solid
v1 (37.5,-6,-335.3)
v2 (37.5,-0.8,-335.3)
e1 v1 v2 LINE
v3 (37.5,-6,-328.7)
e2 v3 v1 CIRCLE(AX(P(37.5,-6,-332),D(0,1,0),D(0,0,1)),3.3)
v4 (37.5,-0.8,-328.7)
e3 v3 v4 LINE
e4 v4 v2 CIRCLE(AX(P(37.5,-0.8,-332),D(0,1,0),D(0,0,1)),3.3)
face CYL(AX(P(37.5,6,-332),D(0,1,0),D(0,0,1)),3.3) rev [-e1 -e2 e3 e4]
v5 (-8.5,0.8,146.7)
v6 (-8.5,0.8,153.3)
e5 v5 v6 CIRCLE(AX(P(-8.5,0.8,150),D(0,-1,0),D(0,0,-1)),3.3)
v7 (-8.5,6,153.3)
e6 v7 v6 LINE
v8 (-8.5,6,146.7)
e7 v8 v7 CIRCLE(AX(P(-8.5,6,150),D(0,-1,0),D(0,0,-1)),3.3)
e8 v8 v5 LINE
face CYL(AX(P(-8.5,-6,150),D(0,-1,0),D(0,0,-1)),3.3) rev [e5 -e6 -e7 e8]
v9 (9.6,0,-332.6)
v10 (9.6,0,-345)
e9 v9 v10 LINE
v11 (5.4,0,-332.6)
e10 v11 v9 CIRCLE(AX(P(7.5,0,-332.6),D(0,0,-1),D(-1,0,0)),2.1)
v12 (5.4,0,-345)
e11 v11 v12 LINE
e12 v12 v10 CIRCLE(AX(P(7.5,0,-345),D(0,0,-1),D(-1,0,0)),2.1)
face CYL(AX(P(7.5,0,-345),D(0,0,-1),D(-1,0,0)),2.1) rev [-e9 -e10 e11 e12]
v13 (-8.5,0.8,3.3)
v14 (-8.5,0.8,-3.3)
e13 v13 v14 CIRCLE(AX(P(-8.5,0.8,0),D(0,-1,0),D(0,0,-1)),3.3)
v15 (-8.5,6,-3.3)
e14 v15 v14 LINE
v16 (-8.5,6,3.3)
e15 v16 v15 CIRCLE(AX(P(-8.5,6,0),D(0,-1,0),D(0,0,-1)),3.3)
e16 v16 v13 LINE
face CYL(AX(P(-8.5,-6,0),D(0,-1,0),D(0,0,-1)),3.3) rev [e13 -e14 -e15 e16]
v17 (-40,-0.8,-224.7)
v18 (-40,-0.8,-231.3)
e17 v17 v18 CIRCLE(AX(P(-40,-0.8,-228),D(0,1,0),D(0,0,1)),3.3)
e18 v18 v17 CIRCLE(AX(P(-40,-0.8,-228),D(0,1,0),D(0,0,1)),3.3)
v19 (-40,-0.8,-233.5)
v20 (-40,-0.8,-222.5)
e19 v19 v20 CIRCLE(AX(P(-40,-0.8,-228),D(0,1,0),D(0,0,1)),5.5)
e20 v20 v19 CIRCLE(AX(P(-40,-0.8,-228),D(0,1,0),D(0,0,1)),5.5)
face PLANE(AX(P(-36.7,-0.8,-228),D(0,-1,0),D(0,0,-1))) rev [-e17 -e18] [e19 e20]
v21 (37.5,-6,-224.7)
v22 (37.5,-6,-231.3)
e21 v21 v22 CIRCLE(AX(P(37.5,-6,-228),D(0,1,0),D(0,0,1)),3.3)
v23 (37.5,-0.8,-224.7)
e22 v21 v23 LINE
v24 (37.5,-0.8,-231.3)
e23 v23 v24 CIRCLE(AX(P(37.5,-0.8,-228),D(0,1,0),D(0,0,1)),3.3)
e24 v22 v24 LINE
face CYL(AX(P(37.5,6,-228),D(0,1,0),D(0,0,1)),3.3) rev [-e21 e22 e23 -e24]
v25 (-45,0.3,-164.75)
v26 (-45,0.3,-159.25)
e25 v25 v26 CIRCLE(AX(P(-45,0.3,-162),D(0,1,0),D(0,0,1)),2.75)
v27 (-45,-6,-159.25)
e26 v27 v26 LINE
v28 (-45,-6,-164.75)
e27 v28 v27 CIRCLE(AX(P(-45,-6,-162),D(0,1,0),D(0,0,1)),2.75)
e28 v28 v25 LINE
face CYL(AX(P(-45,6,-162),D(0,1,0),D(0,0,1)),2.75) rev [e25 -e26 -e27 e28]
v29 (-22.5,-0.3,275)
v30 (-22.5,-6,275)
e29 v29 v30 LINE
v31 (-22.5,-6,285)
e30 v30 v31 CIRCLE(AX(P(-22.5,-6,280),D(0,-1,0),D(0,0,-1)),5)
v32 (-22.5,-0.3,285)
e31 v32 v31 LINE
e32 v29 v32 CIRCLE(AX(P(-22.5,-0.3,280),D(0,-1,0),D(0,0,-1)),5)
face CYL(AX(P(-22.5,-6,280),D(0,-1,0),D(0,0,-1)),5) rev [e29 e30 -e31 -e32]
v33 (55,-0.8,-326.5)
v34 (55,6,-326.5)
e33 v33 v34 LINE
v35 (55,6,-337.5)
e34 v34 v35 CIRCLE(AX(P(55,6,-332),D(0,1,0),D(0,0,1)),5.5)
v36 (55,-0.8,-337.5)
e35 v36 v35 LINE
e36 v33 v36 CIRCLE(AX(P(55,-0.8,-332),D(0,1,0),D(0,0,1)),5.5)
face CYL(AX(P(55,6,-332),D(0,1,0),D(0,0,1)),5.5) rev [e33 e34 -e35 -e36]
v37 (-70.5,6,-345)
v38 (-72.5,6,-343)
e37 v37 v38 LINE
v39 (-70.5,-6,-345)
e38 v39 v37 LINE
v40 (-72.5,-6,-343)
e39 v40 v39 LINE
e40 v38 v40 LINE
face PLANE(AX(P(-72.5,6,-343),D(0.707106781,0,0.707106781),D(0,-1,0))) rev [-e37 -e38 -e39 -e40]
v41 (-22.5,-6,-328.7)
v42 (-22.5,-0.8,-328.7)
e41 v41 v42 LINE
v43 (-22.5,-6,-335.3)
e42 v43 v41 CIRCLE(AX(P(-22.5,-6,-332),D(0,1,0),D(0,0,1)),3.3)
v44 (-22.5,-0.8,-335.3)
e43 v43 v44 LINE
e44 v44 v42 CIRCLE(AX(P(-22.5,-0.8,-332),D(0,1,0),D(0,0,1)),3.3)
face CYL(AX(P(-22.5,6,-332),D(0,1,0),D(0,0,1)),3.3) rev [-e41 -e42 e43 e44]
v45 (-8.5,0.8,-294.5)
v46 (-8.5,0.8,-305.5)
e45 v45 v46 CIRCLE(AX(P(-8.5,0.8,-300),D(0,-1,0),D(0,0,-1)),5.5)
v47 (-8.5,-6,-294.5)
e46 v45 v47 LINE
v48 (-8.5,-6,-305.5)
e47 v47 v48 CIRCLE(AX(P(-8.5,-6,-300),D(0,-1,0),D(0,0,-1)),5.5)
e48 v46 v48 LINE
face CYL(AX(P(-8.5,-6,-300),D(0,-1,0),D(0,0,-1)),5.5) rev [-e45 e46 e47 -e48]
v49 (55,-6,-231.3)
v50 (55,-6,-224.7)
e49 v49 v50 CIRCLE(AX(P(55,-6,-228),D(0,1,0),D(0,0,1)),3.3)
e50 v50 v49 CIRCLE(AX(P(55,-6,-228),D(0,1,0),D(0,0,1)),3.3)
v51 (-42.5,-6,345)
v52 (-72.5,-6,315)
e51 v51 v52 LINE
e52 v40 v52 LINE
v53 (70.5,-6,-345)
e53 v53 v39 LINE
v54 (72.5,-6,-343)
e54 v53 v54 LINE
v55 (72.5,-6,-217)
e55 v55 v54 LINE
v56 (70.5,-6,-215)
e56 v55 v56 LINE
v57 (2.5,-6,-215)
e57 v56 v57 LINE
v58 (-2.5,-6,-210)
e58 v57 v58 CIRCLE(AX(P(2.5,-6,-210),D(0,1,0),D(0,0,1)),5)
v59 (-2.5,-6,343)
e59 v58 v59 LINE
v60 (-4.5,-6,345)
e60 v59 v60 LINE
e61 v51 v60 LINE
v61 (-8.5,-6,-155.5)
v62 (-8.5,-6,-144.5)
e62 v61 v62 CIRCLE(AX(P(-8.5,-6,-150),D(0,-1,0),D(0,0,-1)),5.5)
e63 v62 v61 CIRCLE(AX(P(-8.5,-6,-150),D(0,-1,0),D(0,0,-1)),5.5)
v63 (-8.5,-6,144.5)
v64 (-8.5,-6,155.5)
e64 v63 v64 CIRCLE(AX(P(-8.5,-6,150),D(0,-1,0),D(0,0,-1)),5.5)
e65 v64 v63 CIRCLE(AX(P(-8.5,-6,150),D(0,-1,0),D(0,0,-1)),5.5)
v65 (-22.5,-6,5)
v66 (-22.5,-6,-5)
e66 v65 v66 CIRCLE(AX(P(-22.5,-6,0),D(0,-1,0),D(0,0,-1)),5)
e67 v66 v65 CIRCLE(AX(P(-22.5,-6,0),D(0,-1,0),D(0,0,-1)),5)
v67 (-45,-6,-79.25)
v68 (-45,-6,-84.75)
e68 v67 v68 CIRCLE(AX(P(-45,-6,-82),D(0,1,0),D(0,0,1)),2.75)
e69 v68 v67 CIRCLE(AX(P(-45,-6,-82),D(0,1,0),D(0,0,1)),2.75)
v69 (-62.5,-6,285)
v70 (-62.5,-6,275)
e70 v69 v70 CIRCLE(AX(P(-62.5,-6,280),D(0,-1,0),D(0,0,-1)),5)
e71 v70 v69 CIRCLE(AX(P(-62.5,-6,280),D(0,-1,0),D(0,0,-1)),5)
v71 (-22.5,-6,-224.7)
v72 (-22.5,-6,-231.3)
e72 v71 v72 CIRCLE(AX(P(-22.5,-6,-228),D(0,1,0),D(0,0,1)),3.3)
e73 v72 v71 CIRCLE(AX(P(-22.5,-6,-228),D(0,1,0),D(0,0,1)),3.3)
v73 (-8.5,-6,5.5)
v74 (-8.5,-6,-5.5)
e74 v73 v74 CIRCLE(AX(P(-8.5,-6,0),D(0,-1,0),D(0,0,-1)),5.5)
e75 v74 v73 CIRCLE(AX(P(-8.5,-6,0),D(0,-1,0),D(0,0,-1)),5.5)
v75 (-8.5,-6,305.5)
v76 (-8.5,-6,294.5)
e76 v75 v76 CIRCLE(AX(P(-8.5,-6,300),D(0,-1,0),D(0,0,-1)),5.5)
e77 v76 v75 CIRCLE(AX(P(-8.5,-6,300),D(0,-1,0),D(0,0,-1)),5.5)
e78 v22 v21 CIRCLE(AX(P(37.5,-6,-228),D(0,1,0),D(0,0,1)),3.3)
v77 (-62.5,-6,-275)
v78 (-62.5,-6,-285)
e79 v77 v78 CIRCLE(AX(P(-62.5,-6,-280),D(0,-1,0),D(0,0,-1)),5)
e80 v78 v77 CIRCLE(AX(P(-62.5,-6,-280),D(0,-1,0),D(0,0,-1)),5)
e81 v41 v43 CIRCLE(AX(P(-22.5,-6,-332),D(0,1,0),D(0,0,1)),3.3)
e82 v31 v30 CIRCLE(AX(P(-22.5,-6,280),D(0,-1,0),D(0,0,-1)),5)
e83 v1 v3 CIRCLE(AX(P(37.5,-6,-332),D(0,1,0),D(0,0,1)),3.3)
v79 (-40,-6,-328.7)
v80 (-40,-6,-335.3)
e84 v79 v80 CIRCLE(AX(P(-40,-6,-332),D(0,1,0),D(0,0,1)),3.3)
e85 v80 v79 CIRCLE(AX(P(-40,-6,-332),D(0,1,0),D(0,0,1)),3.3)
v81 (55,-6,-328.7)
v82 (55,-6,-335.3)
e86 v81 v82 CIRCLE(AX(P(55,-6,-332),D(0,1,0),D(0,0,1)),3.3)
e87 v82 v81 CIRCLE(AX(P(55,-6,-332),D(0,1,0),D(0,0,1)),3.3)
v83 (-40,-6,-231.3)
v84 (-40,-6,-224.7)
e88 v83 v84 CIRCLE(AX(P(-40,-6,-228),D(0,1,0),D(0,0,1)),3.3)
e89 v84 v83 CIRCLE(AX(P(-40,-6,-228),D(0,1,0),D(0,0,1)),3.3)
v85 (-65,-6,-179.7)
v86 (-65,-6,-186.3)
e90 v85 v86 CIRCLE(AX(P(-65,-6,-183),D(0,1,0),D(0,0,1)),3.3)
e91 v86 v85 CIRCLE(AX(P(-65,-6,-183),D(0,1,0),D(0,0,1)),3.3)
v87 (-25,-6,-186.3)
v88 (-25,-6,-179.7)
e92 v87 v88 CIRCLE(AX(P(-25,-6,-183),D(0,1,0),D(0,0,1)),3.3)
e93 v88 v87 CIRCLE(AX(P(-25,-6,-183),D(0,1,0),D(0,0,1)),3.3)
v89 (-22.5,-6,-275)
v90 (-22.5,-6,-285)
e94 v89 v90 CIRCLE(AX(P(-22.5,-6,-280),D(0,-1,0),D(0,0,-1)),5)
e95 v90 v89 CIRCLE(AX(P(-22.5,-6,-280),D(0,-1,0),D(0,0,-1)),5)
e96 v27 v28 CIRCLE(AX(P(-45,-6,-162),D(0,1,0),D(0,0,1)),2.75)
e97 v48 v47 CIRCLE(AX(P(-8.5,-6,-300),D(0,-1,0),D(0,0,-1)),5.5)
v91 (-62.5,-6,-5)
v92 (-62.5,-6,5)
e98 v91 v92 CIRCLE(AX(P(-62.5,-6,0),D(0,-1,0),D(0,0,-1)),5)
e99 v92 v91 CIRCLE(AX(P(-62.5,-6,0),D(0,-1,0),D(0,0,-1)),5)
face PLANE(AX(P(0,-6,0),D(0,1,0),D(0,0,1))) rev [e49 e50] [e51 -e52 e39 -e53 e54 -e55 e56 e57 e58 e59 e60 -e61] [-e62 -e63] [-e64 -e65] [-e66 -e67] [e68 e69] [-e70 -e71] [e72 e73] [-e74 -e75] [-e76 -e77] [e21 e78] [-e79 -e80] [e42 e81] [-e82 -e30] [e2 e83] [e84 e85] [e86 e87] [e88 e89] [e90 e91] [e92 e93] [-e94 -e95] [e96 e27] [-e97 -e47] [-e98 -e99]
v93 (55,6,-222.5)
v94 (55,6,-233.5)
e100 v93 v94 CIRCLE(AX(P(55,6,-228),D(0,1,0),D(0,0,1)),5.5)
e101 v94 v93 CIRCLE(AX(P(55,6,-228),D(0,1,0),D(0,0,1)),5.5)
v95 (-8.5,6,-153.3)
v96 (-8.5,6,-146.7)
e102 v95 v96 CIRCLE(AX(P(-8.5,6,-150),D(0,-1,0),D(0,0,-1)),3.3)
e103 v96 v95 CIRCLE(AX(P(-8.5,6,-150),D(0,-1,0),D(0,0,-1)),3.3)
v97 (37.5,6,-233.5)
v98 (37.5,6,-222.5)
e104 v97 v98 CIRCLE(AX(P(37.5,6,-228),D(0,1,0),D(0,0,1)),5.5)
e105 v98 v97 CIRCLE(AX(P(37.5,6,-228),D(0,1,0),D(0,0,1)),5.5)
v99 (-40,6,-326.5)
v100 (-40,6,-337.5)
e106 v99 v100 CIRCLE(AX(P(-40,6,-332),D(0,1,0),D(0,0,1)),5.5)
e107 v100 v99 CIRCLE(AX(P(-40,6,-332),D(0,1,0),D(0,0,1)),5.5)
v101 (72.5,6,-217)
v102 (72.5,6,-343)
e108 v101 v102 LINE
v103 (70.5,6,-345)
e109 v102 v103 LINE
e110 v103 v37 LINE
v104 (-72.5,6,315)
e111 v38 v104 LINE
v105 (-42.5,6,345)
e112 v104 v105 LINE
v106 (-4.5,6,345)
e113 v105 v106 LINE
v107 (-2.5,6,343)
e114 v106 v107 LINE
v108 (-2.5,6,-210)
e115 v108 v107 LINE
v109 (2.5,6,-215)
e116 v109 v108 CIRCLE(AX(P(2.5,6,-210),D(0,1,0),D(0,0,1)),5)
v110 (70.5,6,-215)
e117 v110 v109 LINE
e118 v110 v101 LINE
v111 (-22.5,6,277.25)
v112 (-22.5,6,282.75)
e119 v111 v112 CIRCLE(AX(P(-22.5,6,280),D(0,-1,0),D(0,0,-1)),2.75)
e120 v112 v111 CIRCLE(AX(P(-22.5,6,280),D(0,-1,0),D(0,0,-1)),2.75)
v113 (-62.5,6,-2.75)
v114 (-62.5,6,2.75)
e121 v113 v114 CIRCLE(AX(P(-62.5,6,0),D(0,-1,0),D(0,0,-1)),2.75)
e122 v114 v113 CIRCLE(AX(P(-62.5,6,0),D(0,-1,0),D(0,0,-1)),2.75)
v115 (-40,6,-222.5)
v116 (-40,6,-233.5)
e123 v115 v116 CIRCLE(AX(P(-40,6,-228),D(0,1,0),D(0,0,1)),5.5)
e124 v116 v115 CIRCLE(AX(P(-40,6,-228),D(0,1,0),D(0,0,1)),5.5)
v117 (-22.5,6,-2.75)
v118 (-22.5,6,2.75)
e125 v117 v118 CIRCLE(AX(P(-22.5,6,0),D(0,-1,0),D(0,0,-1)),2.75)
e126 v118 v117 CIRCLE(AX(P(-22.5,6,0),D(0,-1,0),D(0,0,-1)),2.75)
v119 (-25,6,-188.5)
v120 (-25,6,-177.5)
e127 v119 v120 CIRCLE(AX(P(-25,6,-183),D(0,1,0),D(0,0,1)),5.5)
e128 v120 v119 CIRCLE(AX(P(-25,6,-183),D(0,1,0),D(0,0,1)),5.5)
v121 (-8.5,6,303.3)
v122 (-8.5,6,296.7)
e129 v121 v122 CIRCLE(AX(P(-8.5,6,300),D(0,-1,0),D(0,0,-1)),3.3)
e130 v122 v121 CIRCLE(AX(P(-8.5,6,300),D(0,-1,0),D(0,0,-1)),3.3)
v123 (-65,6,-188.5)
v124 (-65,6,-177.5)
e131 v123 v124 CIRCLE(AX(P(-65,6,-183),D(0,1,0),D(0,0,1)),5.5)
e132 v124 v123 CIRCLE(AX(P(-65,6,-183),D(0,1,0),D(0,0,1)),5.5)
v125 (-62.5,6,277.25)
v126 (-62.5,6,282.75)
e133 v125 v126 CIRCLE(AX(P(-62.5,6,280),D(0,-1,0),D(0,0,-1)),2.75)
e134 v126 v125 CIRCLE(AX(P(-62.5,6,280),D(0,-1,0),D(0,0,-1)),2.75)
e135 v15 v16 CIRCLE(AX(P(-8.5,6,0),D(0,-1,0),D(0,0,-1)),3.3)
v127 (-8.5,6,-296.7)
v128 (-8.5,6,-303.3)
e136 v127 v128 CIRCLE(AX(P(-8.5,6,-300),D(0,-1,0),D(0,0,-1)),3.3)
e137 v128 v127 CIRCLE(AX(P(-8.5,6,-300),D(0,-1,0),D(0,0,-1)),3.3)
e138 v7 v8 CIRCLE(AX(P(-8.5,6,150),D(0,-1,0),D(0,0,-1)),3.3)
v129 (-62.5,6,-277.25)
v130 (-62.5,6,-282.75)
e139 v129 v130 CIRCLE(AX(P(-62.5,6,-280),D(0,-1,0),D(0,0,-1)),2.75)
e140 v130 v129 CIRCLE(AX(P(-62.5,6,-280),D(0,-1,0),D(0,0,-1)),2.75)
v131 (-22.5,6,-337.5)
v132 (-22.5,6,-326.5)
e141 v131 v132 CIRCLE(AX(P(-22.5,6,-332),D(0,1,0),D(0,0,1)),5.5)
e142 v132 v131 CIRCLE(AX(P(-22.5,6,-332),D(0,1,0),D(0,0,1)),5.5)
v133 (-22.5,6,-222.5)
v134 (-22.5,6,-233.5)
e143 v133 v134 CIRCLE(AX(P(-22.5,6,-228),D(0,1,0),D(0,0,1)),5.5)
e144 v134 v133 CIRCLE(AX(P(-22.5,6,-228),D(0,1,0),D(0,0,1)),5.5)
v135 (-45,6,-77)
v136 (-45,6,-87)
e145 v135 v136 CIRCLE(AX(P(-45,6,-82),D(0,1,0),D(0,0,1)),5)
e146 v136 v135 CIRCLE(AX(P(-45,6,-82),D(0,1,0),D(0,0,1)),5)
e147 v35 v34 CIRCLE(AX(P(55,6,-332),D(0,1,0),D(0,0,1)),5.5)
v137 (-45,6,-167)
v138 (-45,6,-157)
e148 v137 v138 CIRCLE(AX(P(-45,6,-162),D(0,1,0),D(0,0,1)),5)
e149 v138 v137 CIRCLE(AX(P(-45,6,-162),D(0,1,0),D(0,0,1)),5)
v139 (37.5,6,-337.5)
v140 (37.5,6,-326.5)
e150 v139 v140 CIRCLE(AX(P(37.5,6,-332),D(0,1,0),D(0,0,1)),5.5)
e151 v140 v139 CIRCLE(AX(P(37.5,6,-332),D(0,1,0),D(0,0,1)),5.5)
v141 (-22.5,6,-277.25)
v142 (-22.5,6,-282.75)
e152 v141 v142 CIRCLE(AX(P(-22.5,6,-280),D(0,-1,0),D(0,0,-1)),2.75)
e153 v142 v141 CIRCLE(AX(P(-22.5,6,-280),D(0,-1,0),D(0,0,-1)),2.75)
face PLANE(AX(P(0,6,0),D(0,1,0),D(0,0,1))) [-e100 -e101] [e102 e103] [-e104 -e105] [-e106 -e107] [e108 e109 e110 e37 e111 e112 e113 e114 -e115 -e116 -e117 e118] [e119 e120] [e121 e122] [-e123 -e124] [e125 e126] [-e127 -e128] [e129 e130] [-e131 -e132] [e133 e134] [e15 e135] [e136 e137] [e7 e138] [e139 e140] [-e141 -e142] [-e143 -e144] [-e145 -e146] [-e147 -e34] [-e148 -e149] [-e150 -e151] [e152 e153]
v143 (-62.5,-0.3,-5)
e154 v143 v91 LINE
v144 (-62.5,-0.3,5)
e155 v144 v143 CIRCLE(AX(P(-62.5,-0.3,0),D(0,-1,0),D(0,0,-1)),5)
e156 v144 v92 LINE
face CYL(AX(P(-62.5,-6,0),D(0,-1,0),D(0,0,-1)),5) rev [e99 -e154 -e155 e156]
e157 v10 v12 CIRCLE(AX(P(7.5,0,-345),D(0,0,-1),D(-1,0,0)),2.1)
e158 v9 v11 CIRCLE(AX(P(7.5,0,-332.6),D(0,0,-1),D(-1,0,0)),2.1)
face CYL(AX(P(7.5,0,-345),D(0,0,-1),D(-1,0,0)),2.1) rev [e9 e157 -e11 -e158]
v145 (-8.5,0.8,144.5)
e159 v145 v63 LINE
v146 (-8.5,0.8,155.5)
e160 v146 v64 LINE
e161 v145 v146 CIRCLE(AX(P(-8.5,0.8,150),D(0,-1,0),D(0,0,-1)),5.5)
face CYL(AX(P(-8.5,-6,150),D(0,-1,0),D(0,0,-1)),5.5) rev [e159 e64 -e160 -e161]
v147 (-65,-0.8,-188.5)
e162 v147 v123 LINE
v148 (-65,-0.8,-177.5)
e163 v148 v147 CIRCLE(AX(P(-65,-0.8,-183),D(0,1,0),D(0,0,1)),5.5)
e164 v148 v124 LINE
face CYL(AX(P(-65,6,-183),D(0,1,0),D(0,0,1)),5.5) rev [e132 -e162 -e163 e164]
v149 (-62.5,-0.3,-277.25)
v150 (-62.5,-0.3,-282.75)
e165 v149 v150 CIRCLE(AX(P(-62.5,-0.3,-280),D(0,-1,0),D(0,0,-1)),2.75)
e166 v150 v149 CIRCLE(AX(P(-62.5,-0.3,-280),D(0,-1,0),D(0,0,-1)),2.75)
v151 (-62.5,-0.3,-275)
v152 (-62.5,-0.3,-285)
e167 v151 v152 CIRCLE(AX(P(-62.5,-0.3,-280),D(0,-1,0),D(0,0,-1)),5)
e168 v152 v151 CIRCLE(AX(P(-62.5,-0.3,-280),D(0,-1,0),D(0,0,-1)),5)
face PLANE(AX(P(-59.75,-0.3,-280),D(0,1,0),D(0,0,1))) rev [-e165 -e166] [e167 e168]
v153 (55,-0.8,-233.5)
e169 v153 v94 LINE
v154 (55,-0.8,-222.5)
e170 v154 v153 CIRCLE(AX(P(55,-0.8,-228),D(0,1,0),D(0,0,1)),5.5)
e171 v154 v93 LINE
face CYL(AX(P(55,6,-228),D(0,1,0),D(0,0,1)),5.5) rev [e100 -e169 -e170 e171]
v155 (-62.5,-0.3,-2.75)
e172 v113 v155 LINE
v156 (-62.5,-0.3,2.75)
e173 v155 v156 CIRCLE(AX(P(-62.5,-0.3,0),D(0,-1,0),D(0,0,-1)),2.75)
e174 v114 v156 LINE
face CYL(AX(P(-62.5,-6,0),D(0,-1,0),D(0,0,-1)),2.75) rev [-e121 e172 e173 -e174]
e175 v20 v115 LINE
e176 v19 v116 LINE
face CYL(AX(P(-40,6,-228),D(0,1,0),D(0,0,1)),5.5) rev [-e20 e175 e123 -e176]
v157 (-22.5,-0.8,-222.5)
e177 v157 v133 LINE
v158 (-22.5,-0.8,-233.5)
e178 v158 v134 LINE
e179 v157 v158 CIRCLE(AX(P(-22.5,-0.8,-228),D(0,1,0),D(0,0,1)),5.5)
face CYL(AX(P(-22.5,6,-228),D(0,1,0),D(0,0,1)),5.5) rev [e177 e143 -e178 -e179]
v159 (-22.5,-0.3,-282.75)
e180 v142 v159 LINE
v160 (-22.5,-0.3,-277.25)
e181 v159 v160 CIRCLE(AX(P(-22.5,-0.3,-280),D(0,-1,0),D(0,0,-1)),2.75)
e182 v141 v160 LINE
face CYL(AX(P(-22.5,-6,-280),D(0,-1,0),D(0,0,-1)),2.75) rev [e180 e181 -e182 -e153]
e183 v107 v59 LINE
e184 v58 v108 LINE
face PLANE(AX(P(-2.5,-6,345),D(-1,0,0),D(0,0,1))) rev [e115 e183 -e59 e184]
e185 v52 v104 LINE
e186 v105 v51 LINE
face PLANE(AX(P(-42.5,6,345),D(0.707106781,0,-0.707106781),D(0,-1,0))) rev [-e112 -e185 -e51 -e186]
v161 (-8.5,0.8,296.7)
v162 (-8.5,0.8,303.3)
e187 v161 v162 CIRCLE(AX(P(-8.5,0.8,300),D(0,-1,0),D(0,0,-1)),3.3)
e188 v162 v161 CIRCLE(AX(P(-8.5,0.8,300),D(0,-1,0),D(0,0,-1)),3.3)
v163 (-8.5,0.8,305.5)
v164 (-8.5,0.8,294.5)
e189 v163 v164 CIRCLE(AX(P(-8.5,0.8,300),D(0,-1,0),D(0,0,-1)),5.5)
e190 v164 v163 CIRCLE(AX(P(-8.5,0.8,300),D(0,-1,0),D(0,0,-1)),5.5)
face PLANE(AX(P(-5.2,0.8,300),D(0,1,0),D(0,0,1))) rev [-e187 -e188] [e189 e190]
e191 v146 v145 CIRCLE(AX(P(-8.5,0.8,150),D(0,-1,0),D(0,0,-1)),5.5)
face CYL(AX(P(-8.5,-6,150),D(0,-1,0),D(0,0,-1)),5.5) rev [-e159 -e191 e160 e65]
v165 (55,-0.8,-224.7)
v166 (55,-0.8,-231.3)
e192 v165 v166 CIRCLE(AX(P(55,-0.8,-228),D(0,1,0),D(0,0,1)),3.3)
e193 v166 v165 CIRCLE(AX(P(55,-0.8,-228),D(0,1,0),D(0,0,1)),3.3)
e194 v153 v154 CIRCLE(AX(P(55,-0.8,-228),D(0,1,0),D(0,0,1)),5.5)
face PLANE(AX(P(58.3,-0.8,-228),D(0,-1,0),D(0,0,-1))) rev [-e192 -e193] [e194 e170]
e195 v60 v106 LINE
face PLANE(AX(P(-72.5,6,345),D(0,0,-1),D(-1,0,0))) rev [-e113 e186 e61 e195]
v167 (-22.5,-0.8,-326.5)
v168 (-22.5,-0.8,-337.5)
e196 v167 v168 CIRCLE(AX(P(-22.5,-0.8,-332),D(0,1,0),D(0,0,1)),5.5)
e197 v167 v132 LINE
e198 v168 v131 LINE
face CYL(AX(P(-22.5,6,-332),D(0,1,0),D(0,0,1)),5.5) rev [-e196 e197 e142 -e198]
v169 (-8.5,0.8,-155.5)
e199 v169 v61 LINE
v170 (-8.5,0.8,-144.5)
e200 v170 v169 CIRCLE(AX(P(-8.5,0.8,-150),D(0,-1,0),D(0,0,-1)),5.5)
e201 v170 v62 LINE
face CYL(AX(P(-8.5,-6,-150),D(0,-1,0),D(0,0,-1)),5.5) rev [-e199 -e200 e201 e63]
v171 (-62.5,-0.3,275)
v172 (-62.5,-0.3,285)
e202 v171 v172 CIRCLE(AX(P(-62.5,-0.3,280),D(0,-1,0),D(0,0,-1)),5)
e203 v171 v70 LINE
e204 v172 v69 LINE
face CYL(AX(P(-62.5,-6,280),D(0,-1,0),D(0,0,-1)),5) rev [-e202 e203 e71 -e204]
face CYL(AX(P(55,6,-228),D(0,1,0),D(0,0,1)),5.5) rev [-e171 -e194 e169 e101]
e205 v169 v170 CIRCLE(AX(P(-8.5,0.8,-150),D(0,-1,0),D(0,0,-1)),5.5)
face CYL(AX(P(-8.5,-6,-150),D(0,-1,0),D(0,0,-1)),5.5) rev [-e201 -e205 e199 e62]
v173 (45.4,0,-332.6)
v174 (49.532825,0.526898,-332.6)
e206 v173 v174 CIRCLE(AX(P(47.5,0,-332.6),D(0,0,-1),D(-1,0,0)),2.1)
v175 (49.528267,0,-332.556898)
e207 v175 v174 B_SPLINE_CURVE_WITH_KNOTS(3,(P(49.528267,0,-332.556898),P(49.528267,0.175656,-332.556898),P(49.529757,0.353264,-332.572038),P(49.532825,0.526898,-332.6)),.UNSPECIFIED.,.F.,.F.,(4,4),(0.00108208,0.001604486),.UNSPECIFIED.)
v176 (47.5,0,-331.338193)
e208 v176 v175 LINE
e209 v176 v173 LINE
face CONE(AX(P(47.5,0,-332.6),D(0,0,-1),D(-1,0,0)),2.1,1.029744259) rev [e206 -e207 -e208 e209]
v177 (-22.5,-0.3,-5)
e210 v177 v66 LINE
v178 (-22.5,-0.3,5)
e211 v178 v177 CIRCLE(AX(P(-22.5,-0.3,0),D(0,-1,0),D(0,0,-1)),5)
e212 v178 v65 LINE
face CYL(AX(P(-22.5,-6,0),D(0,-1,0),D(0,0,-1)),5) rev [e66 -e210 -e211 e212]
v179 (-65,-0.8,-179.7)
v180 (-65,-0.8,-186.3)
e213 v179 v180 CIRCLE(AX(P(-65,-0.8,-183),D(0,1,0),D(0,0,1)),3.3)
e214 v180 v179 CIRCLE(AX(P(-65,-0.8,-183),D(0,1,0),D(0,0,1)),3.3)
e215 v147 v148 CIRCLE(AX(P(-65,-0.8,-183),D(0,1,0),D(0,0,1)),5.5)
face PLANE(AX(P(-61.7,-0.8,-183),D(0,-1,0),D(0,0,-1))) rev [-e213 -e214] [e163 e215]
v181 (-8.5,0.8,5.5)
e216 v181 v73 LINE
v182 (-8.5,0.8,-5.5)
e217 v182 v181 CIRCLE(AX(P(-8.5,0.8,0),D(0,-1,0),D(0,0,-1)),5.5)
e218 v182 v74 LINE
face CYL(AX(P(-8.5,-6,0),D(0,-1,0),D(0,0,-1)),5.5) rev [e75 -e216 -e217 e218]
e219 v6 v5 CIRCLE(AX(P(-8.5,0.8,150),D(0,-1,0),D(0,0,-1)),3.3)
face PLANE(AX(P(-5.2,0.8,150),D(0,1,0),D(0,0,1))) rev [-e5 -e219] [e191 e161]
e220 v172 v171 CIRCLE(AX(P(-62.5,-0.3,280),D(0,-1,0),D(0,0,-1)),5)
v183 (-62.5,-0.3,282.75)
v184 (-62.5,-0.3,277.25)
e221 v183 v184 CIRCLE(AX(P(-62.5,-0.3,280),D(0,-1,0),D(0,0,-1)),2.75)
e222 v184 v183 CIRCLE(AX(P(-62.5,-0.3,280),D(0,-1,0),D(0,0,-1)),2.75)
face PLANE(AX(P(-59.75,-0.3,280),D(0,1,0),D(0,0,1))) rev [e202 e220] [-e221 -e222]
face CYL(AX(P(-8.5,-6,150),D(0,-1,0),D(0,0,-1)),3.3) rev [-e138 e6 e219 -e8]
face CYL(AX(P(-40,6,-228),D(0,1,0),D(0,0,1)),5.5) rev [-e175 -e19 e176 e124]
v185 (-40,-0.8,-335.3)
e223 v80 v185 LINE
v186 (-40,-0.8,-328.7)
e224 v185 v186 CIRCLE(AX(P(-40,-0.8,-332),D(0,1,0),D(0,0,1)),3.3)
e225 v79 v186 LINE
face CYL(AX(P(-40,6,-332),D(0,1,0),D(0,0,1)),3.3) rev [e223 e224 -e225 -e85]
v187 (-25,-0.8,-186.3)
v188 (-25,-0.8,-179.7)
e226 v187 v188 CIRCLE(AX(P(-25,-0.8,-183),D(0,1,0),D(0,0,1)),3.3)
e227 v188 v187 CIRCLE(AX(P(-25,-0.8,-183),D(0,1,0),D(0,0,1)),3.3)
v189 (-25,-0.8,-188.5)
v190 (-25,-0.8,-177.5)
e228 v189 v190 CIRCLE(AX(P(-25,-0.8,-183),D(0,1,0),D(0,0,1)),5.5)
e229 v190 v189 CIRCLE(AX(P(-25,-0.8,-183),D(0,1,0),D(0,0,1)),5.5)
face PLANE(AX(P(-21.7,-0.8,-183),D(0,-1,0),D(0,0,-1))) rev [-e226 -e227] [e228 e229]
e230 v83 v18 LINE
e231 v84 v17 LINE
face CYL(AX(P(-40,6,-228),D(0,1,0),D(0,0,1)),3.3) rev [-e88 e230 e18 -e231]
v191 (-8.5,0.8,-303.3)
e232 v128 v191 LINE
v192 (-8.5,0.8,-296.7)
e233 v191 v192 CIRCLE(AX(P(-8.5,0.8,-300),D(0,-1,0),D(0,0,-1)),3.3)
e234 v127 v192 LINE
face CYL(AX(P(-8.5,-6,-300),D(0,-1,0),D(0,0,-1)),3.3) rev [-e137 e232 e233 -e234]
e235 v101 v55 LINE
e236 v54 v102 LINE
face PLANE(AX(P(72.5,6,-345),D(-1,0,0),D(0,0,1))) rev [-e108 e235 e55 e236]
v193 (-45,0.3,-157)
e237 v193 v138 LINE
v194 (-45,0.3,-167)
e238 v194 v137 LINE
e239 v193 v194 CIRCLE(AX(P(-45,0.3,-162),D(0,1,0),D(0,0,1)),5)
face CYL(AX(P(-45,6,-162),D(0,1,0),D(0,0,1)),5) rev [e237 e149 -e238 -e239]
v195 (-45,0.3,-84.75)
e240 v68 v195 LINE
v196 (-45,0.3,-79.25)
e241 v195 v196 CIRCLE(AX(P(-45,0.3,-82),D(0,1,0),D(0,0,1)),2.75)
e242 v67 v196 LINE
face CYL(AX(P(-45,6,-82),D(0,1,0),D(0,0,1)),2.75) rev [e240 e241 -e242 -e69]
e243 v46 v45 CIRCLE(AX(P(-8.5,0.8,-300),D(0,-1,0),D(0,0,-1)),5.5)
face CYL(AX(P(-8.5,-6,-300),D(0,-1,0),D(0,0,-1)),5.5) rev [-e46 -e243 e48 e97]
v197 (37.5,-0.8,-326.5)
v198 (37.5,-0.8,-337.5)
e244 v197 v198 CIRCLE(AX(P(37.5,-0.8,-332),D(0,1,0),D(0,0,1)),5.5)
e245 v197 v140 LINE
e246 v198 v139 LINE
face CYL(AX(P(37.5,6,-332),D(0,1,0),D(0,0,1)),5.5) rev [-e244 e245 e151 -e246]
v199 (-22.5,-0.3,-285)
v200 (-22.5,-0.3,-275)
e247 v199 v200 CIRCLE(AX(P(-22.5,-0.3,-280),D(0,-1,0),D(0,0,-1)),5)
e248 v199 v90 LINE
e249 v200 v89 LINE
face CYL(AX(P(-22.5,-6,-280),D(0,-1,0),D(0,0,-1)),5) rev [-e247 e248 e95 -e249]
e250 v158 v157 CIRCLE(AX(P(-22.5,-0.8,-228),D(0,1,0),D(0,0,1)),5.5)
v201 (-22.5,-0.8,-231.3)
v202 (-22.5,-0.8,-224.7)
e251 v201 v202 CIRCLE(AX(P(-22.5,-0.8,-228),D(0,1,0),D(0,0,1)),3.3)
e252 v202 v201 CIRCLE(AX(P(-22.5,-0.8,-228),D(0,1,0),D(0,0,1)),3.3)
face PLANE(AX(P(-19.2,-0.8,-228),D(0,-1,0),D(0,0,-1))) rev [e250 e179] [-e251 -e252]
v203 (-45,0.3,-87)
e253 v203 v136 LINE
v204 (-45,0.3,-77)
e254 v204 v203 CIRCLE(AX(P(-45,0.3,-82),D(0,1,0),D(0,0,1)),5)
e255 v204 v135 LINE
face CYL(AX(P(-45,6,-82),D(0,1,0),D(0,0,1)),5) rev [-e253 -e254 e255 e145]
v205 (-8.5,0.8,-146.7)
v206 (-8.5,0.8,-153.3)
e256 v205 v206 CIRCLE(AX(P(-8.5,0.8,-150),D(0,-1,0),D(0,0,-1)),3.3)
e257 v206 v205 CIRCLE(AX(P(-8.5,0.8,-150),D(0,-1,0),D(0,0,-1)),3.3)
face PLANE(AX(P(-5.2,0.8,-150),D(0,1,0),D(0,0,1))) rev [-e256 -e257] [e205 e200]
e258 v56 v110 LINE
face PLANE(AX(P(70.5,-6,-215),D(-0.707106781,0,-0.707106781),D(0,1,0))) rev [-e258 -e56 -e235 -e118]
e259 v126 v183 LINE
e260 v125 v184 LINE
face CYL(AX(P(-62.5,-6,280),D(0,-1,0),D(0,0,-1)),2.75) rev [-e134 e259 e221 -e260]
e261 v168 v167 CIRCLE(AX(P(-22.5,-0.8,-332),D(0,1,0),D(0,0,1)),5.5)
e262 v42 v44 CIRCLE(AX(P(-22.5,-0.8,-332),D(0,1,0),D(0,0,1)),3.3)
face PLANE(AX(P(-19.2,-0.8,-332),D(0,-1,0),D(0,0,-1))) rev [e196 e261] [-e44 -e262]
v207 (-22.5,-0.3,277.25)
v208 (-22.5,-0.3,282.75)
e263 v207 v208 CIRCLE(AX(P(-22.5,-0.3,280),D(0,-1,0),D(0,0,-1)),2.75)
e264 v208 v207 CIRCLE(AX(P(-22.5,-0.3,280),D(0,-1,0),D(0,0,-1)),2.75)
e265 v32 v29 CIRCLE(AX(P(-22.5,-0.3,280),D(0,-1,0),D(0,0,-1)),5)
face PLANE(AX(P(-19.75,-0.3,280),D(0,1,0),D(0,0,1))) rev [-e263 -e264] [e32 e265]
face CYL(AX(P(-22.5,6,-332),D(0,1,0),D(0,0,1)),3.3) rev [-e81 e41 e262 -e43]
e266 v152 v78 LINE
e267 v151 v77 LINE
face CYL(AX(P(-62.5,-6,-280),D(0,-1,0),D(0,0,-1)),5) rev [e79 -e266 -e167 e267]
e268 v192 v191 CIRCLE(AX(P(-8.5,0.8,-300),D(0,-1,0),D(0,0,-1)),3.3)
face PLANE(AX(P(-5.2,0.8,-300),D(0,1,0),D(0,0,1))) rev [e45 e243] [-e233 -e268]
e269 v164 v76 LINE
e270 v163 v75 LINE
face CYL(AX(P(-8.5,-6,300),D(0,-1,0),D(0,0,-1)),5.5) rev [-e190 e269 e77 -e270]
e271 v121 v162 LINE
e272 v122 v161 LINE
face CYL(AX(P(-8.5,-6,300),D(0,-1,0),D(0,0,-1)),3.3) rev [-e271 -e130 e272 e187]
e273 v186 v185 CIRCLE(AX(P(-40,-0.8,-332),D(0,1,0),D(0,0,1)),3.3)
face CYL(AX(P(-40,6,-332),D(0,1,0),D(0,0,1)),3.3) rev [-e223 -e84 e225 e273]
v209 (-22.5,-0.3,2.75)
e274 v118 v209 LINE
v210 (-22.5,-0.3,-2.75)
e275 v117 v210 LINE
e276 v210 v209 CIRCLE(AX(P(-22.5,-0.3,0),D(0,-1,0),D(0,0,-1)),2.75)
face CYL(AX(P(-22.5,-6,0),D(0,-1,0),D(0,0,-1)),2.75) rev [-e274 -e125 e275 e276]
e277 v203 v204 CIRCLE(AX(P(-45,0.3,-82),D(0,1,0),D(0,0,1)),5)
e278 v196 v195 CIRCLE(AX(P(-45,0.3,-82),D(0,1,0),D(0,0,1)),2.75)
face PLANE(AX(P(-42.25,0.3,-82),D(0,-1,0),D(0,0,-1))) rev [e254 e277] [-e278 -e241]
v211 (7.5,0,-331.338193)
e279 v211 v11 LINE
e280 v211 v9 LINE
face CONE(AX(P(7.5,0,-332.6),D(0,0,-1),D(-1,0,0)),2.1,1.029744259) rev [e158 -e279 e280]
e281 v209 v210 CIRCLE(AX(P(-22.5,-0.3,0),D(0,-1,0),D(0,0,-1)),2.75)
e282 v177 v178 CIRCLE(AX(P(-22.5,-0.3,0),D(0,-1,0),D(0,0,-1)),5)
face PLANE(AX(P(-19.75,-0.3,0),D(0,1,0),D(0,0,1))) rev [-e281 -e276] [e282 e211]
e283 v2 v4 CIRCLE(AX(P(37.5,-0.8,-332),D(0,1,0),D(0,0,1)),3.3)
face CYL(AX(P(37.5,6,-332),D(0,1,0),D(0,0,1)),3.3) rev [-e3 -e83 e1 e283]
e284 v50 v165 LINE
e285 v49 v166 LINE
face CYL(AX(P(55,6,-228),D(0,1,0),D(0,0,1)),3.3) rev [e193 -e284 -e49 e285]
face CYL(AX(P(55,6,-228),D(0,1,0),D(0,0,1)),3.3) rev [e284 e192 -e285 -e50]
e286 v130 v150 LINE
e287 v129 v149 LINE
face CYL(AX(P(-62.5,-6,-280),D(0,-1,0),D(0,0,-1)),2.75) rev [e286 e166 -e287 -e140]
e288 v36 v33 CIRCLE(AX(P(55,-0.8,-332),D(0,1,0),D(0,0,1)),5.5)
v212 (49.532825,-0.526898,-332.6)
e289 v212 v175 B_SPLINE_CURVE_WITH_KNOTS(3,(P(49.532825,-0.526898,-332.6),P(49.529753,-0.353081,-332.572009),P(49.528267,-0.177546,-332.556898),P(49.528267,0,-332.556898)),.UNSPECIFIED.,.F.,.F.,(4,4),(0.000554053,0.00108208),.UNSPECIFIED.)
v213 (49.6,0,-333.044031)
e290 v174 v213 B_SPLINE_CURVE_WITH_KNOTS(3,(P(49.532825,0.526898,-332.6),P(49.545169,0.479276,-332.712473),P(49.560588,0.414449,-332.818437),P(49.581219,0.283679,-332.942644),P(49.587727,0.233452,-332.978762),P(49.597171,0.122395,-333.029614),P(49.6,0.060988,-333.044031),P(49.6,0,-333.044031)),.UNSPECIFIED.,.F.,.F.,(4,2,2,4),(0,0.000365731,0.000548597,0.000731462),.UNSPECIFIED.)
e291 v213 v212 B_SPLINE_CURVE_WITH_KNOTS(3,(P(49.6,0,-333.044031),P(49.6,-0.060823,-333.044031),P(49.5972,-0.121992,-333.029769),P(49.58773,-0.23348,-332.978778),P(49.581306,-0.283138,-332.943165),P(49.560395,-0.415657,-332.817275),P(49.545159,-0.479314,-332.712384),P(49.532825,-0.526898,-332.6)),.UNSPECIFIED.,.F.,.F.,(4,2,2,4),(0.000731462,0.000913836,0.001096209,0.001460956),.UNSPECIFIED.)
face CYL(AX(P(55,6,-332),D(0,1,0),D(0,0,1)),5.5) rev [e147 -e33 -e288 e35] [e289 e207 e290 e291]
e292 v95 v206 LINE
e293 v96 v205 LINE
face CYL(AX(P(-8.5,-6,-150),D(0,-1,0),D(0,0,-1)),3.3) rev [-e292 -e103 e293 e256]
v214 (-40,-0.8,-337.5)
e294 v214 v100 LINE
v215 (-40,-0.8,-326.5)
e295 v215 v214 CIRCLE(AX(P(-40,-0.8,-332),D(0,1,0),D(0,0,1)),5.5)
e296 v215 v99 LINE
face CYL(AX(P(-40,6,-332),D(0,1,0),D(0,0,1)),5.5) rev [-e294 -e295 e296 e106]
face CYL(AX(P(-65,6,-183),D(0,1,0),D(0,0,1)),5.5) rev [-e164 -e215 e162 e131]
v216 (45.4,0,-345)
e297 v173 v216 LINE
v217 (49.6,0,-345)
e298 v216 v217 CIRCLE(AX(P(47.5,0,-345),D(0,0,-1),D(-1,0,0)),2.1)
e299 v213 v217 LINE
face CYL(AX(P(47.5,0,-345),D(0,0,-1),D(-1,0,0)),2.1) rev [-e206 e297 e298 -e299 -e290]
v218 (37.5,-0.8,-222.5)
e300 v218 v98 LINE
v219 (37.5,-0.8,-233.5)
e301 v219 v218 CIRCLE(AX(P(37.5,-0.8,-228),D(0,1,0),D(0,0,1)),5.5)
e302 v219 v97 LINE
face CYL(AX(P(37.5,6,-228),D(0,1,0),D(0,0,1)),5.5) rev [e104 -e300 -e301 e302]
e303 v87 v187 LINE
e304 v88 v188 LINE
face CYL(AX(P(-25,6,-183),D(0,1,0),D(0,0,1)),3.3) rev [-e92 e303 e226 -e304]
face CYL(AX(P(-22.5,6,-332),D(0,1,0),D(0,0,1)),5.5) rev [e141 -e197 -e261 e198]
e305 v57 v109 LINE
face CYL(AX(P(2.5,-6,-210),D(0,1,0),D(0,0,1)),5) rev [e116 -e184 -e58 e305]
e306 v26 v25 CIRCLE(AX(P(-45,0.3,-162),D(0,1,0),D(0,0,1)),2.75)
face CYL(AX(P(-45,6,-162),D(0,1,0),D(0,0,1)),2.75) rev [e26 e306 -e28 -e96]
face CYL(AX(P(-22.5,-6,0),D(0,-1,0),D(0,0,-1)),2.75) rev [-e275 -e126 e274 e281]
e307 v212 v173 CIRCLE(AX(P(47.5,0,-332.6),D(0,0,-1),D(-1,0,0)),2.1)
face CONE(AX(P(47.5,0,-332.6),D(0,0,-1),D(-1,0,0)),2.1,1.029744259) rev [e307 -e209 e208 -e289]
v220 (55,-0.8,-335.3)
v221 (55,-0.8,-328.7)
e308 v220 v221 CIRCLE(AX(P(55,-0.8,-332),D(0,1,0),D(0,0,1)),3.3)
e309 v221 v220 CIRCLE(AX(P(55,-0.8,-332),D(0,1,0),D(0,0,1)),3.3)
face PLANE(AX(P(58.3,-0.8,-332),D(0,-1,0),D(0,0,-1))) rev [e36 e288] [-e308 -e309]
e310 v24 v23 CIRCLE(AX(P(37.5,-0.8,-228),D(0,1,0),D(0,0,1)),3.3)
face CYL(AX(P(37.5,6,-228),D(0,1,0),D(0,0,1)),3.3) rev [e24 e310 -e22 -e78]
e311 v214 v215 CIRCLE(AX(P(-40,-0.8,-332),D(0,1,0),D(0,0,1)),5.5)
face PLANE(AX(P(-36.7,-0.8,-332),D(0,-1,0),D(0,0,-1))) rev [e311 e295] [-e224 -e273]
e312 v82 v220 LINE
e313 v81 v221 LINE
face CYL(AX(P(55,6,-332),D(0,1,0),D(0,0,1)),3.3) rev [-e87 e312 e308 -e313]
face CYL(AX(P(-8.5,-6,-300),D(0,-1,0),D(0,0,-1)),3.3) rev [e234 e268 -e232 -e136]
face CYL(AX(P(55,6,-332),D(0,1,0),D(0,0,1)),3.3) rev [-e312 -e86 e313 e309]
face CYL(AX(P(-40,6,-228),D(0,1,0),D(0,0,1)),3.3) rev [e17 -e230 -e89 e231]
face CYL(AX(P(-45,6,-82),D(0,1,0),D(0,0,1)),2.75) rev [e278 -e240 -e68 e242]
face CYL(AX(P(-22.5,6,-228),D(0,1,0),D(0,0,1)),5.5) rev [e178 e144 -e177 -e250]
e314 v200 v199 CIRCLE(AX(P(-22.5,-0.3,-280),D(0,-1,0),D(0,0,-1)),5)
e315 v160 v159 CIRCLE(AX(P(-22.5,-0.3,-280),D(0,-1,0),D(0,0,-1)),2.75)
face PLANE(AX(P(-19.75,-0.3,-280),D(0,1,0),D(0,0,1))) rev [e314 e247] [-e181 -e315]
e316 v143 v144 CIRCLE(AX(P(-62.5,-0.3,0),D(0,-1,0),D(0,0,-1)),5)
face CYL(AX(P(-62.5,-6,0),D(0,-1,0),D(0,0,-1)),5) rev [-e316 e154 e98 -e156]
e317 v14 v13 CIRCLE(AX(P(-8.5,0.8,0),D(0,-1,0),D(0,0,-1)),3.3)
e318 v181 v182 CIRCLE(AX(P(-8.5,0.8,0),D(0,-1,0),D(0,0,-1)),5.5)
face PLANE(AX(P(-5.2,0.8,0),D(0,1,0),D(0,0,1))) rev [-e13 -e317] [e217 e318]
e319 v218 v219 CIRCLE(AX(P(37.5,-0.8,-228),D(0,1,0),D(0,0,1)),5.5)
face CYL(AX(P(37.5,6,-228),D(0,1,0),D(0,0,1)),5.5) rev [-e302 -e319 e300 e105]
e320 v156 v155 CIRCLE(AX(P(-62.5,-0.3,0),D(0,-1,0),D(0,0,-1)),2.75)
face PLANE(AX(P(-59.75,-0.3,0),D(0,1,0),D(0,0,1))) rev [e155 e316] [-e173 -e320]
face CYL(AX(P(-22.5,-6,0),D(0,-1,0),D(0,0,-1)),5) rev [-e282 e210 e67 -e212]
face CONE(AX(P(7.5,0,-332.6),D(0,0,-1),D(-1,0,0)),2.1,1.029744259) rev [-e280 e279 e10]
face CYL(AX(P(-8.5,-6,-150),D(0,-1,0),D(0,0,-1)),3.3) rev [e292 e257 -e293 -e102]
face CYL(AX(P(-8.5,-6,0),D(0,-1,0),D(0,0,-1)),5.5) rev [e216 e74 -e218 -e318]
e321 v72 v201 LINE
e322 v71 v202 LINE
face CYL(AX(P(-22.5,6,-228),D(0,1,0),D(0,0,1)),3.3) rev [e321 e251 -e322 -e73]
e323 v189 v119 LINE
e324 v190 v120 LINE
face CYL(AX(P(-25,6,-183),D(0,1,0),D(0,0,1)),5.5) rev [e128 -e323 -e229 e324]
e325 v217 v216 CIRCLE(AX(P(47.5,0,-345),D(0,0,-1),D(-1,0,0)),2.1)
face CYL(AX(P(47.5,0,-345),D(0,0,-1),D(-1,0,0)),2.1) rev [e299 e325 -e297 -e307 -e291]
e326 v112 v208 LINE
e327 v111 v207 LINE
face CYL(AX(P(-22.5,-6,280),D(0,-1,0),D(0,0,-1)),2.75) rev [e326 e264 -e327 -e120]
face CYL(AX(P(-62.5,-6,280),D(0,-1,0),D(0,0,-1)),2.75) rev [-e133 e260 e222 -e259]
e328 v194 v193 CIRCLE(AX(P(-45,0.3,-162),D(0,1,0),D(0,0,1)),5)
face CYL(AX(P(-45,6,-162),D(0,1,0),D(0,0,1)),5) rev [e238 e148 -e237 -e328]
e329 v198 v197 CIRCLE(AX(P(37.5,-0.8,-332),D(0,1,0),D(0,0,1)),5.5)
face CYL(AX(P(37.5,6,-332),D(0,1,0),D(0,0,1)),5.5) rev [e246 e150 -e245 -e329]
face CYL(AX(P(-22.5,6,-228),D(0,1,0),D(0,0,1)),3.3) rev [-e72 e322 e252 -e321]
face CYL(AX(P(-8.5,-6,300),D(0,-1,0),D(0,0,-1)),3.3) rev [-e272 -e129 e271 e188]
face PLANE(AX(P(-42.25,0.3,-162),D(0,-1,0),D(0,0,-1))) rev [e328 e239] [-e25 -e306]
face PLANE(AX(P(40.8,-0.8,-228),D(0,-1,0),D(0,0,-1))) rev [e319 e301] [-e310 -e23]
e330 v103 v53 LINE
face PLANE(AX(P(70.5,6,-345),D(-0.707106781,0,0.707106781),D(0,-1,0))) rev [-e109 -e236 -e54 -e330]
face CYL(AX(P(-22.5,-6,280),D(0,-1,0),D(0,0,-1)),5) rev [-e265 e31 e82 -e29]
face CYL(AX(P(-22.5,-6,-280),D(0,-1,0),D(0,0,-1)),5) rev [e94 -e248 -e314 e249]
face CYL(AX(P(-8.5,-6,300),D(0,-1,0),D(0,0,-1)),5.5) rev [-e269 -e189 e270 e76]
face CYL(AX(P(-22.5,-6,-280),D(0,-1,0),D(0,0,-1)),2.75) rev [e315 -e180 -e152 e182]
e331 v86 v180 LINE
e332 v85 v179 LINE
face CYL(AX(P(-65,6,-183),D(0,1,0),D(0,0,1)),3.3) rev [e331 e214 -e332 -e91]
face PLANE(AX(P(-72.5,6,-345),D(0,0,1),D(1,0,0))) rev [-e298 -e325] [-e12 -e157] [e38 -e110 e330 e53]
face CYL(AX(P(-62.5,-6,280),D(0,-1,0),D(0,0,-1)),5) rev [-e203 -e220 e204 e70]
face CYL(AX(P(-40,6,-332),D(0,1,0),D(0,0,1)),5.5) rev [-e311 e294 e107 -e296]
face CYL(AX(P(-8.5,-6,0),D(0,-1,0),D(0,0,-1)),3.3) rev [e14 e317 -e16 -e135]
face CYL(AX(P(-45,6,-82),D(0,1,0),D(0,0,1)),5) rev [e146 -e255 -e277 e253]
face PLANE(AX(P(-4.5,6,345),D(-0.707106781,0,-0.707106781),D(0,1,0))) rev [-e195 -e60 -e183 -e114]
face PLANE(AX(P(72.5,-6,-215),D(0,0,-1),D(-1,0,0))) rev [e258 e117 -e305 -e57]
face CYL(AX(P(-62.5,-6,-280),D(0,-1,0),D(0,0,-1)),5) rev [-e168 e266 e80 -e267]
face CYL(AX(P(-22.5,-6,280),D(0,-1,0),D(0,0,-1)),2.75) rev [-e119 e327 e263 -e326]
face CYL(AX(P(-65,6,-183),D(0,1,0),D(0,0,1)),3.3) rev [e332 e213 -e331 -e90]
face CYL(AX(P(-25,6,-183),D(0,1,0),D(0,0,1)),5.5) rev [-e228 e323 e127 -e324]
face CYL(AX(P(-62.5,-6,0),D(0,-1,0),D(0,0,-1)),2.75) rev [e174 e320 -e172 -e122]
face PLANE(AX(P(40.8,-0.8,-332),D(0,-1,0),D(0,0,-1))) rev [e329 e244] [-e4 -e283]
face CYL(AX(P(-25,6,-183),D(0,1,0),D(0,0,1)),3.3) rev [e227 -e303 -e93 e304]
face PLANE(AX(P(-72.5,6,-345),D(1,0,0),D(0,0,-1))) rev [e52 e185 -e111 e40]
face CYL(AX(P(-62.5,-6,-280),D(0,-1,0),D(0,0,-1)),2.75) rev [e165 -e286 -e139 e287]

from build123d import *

# Parameters (mm, degrees)
SKETCH_1_W                = 145
SKETCH_1_H                = 690
EXTRUDE_1_DEPTH           = 6
CUT_EXTRUDE_1_DEPTH       = 353.739634858
CHAMFER_1_SIZE            = 2
HOLE_WIZARD_1_D           = 6.6
HOLE_WIZARD_1_CBORE_D     = 11
HOLE_WIZARD_1_CBORE_DEPTH = 6.8
HOLE_WIZARD_2_D           = 6.6
HOLE_WIZARD_2_CBORE_D     = 11
HOLE_WIZARD_2_CBORE_DEPTH = 6.8
HOLE_WIZARD_3_D           = 5.5
HOLE_WIZARD_3_CBORE_D     = 10
HOLE_WIZARD_3_CBORE_DEPTH = 5.7
HOLE_WIZARD_M5_1_D        = 4.2
HOLE_WIZARD_M5_1_DEPTH    = 12.4
HOLE_WIZARD_M5_1_TIP      = 1.2618073
HOLE_WIZARD_4_D           = 6.6
HOLE_WIZARD_4_CBORE_D     = 11
HOLE_WIZARD_4_CBORE_DEPTH = 6.8
HOLE_WIZARD_5_D           = 5.5
HOLE_WIZARD_5_CBORE_D     = 10
HOLE_WIZARD_5_CBORE_DEPTH = 5.7
CHAMFER_2_SIZE            = 30


with BuildPart() as part:
    # 草图1 → 凸台-拉伸1 (new, symmetric)
    with BuildSketch(Plane(origin=(0, 0, 0), x_dir=(1, 0, 0), z_dir=(0, 1, 0))):
        Rectangle(SKETCH_1_W, SKETCH_1_H)
    extrude(amount=EXTRUDE_1_DEPTH, both=True)

    # 草图2 → 切除-拉伸1 (cut, through all)
    with BuildSketch(Plane(origin=(0, 6, 0), x_dir=(1, 0, 0), z_dir=(0, 1, 0))):
        with BuildLine():
            Line((72.5, -345), (-2.5, -345))
            Line((-2.5, -345), (-2.5, 210))
            ThreePointArc((-2.5, 210), (-1.035533906, 213.535533906), (2.5, 215))
            Line((2.5, 215), (72.5, 215))
            Line((72.5, 215), (72.5, -345))
        make_face()
    extrude(amount=-CUT_EXTRUDE_1_DEPTH, mode=Mode.SUBTRACT)

    # 倒角1
    chamfer_1_edges = [part.edges().sort_by_distance(p)[0] for p in [
        (72.5, 0, -215),
        (-2.5, 0, 345),
        (-72.5, 0, -345),
        (72.5, 0, -345),
    ]]
    chamfer(chamfer_1_edges, length=CHAMFER_1_SIZE)

    # 打孔尺寸(%根据)内六角圆柱头螺钉的类型1 (through all)
    with Locations(Plane(origin=(0, 6, 0), x_dir=(1, 0, 0), z_dir=(0, 1, 0))):
        with Locations((-40, 228), (-22.5, 228), (37.5, 228), (55, 228), (55, 332), (37.5, 332), (-22.5, 332), (-40, 332)):
            CounterBoreHole(HOLE_WIZARD_1_D / 2, HOLE_WIZARD_1_CBORE_D / 2, HOLE_WIZARD_1_CBORE_DEPTH)

    # 打孔尺寸(%根据)内六角圆柱头螺钉的类型2 (through all)
    with Locations(Plane(origin=(0, -6, 0), x_dir=(-1, 0, 0), z_dir=(0, -1, 0))):
        with Locations((8.5, 300), (8.5, 150), (8.5, 0), (8.5, -150), (8.5, -300)):
            CounterBoreHole(HOLE_WIZARD_2_D / 2, HOLE_WIZARD_2_CBORE_D / 2, HOLE_WIZARD_2_CBORE_DEPTH)

    # 打孔尺寸(%根据)内六角圆柱头螺钉的类型3 (through all)
    with Locations(Plane(origin=(0, -6, 0), x_dir=(-1, 0, 0), z_dir=(0, -1, 0))):
        with Locations((22.5, 280), (62.5, 280), (22.5, 0), (62.5, 0), (22.5, -280), (62.5, -280)):
            CounterBoreHole(HOLE_WIZARD_3_D / 2, HOLE_WIZARD_3_CBORE_D / 2, HOLE_WIZARD_3_CBORE_DEPTH)

    # M5 螺纹孔1
    with Locations(Plane(origin=(0, 0, -345), x_dir=(-1, 0, 0), z_dir=(0, 0, -1))):
        with Locations((-7.5, 0), (-47.5, 0)):
            Hole(HOLE_WIZARD_M5_1_D / 2, depth=HOLE_WIZARD_M5_1_DEPTH)
            with Locations((0, 0, -(HOLE_WIZARD_M5_1_DEPTH + HOLE_WIZARD_M5_1_TIP / 2))):  # 118° drill point
                Cone(0, HOLE_WIZARD_M5_1_D / 2, HOLE_WIZARD_M5_1_TIP, mode=Mode.SUBTRACT)

    # 打孔尺寸(%根据)内六角圆柱头螺钉的类型4 (through all)
    with Locations(Plane(origin=(0, 6, 0), x_dir=(1, 0, 0), z_dir=(0, 1, 0))):
        with Locations((-65, 183), (-25, 183)):
            CounterBoreHole(HOLE_WIZARD_4_D / 2, HOLE_WIZARD_4_CBORE_D / 2, HOLE_WIZARD_4_CBORE_DEPTH)

    # 打孔尺寸(%根据)内六角圆柱头螺钉的类型5 (through all)
    with Locations(Plane(origin=(0, 6, 0), x_dir=(1, 0, 0), z_dir=(0, 1, 0))):
        with Locations((-45, 162), (-45, 82)):
            CounterBoreHole(HOLE_WIZARD_5_D / 2, HOLE_WIZARD_5_CBORE_D / 2, HOLE_WIZARD_5_CBORE_DEPTH)

    # 倒角2
    chamfer_2_edges = [part.edges().sort_by_distance(p)[0] for p in [
        (-72.5, 0, 345),
    ]]
    chamfer(chamfer_2_edges, length=CHAMFER_2_SIZE)


solid = part.part
